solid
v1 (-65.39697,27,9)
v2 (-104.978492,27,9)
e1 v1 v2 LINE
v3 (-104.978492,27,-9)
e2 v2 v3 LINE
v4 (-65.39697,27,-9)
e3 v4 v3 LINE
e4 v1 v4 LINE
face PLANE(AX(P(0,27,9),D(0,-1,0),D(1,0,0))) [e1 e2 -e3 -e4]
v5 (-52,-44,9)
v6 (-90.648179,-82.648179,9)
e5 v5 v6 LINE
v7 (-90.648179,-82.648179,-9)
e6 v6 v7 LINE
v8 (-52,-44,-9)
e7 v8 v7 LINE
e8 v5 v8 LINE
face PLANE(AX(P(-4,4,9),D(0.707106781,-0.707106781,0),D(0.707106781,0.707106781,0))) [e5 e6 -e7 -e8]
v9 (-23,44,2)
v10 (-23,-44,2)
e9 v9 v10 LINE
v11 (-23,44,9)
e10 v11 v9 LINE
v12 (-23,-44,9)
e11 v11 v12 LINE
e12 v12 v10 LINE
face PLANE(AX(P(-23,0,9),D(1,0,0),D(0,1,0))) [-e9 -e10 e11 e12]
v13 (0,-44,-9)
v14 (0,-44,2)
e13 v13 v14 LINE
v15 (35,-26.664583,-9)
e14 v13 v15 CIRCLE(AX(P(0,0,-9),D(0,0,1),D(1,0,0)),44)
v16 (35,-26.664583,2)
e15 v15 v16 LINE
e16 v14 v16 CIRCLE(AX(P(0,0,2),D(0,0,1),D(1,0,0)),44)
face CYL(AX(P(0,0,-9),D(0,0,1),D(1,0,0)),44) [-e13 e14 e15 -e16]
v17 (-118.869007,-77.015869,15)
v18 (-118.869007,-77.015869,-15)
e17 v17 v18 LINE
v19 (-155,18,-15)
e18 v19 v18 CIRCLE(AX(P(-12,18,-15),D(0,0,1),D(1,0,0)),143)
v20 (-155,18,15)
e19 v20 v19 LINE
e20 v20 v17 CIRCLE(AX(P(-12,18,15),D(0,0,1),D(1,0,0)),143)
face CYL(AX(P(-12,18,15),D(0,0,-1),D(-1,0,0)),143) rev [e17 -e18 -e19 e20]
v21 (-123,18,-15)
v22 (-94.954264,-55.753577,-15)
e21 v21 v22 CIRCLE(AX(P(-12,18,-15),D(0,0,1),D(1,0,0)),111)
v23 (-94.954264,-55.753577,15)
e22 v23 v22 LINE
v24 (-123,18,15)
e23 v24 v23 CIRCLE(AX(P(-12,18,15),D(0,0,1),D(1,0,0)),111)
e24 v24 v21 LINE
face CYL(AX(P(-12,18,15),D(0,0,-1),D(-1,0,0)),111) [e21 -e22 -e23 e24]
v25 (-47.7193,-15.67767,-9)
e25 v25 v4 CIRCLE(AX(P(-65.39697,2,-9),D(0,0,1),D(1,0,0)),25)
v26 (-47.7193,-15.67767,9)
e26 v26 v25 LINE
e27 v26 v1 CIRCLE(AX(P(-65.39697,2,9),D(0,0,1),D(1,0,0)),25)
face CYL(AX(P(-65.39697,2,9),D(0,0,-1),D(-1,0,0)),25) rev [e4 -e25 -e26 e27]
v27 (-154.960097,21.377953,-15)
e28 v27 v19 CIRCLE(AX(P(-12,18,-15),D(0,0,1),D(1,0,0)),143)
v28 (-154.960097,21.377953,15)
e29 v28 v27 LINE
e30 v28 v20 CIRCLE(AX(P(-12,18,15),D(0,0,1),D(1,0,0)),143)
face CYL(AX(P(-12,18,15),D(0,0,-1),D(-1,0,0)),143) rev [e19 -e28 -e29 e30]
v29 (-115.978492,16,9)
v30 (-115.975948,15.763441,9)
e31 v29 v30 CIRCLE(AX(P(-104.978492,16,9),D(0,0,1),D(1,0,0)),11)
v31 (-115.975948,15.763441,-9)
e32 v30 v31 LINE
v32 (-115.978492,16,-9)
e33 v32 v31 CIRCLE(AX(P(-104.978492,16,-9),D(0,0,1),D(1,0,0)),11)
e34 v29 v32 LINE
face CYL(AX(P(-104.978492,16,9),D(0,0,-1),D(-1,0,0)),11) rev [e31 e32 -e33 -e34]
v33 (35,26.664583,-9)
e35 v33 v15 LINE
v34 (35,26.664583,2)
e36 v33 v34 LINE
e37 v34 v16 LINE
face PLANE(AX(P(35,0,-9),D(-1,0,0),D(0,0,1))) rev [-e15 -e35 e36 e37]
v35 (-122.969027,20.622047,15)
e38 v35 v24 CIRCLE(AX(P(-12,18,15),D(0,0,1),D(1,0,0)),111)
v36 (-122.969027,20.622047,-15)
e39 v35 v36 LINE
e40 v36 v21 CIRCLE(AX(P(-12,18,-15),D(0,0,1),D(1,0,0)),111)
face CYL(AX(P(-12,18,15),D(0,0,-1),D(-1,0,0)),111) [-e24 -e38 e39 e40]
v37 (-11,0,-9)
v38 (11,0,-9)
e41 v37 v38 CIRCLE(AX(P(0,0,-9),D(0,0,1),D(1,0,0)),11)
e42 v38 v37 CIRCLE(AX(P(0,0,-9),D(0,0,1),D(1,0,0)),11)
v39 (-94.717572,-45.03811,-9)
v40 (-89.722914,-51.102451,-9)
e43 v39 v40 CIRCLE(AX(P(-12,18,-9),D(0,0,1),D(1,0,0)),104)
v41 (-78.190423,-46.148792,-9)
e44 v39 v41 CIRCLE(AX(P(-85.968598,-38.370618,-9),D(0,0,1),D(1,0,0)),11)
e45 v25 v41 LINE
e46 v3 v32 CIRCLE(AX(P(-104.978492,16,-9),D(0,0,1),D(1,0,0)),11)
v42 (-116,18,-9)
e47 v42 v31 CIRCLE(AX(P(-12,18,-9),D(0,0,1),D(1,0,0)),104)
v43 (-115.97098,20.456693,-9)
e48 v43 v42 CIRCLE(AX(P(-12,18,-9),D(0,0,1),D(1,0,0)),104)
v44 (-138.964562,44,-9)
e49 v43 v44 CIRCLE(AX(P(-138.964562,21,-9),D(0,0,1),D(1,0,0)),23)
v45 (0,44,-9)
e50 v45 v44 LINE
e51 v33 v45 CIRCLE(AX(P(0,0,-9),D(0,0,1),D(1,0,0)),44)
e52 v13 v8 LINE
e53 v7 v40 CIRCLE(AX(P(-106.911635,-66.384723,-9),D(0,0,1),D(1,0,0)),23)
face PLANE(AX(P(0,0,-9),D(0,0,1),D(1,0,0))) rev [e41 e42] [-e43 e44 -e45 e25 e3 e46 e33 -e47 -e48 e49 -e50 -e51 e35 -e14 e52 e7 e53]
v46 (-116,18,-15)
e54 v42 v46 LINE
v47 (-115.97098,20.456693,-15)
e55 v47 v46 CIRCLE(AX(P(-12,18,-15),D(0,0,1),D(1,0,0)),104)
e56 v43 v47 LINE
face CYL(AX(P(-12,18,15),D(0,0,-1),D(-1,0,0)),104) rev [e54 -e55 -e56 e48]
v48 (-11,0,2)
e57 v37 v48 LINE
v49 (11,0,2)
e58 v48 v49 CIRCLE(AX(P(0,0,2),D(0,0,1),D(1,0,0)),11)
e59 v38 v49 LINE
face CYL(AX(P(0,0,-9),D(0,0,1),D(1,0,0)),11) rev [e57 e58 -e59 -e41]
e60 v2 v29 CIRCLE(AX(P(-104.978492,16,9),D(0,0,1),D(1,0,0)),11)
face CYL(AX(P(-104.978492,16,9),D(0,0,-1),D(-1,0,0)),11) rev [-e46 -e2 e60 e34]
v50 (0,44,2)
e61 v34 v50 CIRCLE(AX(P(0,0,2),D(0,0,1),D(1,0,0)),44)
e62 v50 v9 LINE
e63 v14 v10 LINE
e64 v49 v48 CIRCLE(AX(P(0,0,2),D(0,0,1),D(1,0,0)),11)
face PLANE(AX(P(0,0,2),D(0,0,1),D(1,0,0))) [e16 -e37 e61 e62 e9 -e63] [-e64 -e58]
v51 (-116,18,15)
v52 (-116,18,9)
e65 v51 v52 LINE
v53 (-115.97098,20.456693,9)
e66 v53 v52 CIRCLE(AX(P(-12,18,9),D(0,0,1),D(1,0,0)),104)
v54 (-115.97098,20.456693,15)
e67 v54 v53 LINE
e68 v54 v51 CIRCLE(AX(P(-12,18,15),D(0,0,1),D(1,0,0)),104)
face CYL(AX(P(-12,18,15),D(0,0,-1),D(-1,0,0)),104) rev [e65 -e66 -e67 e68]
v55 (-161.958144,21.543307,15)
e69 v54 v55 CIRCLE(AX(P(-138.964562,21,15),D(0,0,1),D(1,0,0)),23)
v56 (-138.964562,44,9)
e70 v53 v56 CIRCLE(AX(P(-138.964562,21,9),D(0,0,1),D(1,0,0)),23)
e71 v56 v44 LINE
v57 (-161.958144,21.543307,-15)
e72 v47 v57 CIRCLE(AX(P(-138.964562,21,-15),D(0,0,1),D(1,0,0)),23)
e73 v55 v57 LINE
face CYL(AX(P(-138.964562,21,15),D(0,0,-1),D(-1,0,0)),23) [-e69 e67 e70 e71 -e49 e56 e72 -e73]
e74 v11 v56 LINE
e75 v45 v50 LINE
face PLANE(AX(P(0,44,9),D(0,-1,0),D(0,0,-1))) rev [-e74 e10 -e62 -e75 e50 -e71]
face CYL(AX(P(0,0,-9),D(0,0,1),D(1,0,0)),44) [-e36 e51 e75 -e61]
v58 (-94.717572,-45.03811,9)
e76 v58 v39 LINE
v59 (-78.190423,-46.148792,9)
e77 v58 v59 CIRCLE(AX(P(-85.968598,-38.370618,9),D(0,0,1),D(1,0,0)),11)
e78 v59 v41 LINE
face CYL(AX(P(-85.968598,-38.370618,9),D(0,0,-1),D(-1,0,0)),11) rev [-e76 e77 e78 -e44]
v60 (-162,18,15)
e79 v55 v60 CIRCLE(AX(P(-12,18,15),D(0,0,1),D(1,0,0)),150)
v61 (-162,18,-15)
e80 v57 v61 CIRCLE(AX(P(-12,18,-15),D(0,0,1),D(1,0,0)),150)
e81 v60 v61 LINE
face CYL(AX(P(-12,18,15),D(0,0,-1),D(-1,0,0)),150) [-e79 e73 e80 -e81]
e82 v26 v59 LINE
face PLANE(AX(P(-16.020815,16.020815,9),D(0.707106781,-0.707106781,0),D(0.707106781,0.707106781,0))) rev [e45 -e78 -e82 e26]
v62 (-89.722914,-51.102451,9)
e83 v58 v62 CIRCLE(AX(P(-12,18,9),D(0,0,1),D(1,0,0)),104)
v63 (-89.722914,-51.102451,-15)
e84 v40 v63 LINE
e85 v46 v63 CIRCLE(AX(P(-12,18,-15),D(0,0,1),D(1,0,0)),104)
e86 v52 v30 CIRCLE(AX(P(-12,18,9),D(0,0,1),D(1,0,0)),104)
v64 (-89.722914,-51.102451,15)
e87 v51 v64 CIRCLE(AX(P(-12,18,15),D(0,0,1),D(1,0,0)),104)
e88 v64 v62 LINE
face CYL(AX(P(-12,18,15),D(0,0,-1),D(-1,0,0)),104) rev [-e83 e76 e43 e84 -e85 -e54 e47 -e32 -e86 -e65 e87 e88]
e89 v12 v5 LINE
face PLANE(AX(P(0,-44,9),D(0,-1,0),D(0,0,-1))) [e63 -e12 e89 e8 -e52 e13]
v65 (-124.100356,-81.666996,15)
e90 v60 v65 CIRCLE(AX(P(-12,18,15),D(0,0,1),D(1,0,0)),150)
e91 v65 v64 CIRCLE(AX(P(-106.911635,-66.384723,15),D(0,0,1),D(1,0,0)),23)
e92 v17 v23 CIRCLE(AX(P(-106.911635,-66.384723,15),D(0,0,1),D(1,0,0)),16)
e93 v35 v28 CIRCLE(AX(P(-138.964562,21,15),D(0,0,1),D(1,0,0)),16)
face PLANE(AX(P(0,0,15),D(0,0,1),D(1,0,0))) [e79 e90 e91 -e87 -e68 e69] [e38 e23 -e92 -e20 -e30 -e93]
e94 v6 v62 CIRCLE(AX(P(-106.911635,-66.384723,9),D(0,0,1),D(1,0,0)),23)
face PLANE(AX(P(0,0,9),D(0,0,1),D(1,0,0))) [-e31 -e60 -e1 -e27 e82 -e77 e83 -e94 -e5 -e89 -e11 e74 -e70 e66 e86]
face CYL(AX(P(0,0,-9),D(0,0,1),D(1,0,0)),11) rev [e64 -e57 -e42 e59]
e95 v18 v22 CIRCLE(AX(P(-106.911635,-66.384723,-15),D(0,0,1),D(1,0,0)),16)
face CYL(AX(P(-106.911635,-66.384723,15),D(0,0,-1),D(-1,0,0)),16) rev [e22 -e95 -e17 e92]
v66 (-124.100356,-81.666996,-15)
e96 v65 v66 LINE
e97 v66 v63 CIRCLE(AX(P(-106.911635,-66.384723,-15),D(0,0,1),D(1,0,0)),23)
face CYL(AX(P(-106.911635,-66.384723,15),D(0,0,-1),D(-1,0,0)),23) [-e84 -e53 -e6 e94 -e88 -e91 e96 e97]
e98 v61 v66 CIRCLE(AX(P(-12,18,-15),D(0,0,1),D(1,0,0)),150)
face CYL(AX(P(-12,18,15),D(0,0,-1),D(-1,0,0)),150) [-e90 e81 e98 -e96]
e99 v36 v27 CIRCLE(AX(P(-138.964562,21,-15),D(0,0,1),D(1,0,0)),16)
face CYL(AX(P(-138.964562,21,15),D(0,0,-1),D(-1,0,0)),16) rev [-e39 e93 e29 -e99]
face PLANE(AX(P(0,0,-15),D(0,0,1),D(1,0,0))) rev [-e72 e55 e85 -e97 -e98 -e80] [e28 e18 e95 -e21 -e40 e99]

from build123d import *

# Parameters (mm, degrees)
CLAMP_LOOP_30MM_DEPTH   = 15
SUPPORT_WEB_18MM_DEPTH  = 9
MOUNTING_LUG_DEPTH      = 2
MOUNTING_LUG_DEPTH_BACK = 9
SKETCH1_4_R             = 11


with BuildPart() as part:
    # Bracket Profile Sketch → Clamp Loop 30mm (new, symmetric)
    with BuildSketch(Plane.XY):
        with BuildLine():
            ThreePointArc((-161.958144077, 21.543307087), (-152.82526794, -33.65504728), (-124.10035648, -81.666995927))
            ThreePointArc((-124.10035648, -81.666995927), (-91.629362444, -83.573444545), (-89.722913826, -51.102450509))
            ThreePointArc((-89.722913826, -51.102450509), (-109.638852439, -17.814166114), (-115.970979893, 20.456692913))
            ThreePointArc((-115.970979893, 20.456692913), (-138.421254898, 43.993582092), (-161.958144077, 21.543307087))
        make_face()
        with BuildLine():
            ThreePointArc((-122.969026617, 20.622047244), (-138.586609229, 36.995535368), (-154.960097353, 21.377952756))
            ThreePointArc((-154.960097353, 21.377952756), (-146.253422103, -31.244478407), (-118.869006511, -77.01586945))
            ThreePointArc((-118.869006511, -77.01586945), (-96.280488921, -78.342094576), (-94.954263795, -55.753576986))
            ThreePointArc((-94.954263795, -55.753576986), (-116.210698276, -20.224734987), (-122.969026617, 20.622047244))
        make_face(mode=Mode.SUBTRACT)
    extrude(amount=CLAMP_LOOP_30MM_DEPTH, both=True)

    # Sketch1_3 → Support Web 18mm (add, symmetric)
    with BuildSketch(Plane.XY):
        with BuildLine():
            Line((-23, -44), (-23, 44))
            Line((-23, 44), (-138.964561985, 44))
            ThreePointArc((-138.964561985, 44), (-122.51013913, 37.070219927), (-115.970979893, 20.456692913))
            ThreePointArc((-115.970979893, 20.456692913), (-115.999941726, 18.110094916), (-115.975948196, 15.76344086))
            ThreePointArc((-115.975948196, 15.76344086), (-112.839858129, 23.694083749), (-104.978492137, 27))
            Line((-104.978492137, 27), (-65.39696962, 27))
            ThreePointArc((-65.39696962, 27), (-42.299981307, 11.567085809), (-47.71930009, -15.67766953))
            Line((-47.71930009, -15.67766953), (-78.190423053, -46.148792492))
            ThreePointArc((-78.190423053, -46.148792492), (-86.706172416, -49.345862018), (-94.717571561, -45.038110339))
            ThreePointArc((-94.717571561, -45.038110339), (-92.277527324, -48.11746068), (-89.722913826, -51.102450509))
            ThreePointArc((-89.722913826, -51.102450509), (-83.921522259, -67.059044464), (-90.648179186, -82.648179186))
            Line((-90.648179186, -82.648179186), (-52, -44))
            Line((-52, -44), (-23, -44))
        make_face()
    extrude(amount=SUPPORT_WEB_18MM_DEPTH, both=True)

    # Sketch1_4 → Mounting Lug (add, two sides: drawn at the far end of the back side and taken through both)
    with BuildSketch(Plane.XY.offset(-MOUNTING_LUG_DEPTH_BACK)):
        with BuildLine():
            ThreePointArc((35, 26.664583252), (19.528931575, 39.428680317), (0, 44))
            Line((0, 44), (-23, 44))
            Line((-23, 44), (-23, -44))
            Line((-23, -44), (0, -44))
            ThreePointArc((0, -44), (19.528931575, -39.428680317), (35, -26.664583252))
            Line((35, -26.664583252), (35, 26.664583252))
        make_face()
        Circle(SKETCH1_4_R, mode=Mode.SUBTRACT)
    extrude(amount=MOUNTING_LUG_DEPTH + MOUNTING_LUG_DEPTH_BACK)


solid = part.part
